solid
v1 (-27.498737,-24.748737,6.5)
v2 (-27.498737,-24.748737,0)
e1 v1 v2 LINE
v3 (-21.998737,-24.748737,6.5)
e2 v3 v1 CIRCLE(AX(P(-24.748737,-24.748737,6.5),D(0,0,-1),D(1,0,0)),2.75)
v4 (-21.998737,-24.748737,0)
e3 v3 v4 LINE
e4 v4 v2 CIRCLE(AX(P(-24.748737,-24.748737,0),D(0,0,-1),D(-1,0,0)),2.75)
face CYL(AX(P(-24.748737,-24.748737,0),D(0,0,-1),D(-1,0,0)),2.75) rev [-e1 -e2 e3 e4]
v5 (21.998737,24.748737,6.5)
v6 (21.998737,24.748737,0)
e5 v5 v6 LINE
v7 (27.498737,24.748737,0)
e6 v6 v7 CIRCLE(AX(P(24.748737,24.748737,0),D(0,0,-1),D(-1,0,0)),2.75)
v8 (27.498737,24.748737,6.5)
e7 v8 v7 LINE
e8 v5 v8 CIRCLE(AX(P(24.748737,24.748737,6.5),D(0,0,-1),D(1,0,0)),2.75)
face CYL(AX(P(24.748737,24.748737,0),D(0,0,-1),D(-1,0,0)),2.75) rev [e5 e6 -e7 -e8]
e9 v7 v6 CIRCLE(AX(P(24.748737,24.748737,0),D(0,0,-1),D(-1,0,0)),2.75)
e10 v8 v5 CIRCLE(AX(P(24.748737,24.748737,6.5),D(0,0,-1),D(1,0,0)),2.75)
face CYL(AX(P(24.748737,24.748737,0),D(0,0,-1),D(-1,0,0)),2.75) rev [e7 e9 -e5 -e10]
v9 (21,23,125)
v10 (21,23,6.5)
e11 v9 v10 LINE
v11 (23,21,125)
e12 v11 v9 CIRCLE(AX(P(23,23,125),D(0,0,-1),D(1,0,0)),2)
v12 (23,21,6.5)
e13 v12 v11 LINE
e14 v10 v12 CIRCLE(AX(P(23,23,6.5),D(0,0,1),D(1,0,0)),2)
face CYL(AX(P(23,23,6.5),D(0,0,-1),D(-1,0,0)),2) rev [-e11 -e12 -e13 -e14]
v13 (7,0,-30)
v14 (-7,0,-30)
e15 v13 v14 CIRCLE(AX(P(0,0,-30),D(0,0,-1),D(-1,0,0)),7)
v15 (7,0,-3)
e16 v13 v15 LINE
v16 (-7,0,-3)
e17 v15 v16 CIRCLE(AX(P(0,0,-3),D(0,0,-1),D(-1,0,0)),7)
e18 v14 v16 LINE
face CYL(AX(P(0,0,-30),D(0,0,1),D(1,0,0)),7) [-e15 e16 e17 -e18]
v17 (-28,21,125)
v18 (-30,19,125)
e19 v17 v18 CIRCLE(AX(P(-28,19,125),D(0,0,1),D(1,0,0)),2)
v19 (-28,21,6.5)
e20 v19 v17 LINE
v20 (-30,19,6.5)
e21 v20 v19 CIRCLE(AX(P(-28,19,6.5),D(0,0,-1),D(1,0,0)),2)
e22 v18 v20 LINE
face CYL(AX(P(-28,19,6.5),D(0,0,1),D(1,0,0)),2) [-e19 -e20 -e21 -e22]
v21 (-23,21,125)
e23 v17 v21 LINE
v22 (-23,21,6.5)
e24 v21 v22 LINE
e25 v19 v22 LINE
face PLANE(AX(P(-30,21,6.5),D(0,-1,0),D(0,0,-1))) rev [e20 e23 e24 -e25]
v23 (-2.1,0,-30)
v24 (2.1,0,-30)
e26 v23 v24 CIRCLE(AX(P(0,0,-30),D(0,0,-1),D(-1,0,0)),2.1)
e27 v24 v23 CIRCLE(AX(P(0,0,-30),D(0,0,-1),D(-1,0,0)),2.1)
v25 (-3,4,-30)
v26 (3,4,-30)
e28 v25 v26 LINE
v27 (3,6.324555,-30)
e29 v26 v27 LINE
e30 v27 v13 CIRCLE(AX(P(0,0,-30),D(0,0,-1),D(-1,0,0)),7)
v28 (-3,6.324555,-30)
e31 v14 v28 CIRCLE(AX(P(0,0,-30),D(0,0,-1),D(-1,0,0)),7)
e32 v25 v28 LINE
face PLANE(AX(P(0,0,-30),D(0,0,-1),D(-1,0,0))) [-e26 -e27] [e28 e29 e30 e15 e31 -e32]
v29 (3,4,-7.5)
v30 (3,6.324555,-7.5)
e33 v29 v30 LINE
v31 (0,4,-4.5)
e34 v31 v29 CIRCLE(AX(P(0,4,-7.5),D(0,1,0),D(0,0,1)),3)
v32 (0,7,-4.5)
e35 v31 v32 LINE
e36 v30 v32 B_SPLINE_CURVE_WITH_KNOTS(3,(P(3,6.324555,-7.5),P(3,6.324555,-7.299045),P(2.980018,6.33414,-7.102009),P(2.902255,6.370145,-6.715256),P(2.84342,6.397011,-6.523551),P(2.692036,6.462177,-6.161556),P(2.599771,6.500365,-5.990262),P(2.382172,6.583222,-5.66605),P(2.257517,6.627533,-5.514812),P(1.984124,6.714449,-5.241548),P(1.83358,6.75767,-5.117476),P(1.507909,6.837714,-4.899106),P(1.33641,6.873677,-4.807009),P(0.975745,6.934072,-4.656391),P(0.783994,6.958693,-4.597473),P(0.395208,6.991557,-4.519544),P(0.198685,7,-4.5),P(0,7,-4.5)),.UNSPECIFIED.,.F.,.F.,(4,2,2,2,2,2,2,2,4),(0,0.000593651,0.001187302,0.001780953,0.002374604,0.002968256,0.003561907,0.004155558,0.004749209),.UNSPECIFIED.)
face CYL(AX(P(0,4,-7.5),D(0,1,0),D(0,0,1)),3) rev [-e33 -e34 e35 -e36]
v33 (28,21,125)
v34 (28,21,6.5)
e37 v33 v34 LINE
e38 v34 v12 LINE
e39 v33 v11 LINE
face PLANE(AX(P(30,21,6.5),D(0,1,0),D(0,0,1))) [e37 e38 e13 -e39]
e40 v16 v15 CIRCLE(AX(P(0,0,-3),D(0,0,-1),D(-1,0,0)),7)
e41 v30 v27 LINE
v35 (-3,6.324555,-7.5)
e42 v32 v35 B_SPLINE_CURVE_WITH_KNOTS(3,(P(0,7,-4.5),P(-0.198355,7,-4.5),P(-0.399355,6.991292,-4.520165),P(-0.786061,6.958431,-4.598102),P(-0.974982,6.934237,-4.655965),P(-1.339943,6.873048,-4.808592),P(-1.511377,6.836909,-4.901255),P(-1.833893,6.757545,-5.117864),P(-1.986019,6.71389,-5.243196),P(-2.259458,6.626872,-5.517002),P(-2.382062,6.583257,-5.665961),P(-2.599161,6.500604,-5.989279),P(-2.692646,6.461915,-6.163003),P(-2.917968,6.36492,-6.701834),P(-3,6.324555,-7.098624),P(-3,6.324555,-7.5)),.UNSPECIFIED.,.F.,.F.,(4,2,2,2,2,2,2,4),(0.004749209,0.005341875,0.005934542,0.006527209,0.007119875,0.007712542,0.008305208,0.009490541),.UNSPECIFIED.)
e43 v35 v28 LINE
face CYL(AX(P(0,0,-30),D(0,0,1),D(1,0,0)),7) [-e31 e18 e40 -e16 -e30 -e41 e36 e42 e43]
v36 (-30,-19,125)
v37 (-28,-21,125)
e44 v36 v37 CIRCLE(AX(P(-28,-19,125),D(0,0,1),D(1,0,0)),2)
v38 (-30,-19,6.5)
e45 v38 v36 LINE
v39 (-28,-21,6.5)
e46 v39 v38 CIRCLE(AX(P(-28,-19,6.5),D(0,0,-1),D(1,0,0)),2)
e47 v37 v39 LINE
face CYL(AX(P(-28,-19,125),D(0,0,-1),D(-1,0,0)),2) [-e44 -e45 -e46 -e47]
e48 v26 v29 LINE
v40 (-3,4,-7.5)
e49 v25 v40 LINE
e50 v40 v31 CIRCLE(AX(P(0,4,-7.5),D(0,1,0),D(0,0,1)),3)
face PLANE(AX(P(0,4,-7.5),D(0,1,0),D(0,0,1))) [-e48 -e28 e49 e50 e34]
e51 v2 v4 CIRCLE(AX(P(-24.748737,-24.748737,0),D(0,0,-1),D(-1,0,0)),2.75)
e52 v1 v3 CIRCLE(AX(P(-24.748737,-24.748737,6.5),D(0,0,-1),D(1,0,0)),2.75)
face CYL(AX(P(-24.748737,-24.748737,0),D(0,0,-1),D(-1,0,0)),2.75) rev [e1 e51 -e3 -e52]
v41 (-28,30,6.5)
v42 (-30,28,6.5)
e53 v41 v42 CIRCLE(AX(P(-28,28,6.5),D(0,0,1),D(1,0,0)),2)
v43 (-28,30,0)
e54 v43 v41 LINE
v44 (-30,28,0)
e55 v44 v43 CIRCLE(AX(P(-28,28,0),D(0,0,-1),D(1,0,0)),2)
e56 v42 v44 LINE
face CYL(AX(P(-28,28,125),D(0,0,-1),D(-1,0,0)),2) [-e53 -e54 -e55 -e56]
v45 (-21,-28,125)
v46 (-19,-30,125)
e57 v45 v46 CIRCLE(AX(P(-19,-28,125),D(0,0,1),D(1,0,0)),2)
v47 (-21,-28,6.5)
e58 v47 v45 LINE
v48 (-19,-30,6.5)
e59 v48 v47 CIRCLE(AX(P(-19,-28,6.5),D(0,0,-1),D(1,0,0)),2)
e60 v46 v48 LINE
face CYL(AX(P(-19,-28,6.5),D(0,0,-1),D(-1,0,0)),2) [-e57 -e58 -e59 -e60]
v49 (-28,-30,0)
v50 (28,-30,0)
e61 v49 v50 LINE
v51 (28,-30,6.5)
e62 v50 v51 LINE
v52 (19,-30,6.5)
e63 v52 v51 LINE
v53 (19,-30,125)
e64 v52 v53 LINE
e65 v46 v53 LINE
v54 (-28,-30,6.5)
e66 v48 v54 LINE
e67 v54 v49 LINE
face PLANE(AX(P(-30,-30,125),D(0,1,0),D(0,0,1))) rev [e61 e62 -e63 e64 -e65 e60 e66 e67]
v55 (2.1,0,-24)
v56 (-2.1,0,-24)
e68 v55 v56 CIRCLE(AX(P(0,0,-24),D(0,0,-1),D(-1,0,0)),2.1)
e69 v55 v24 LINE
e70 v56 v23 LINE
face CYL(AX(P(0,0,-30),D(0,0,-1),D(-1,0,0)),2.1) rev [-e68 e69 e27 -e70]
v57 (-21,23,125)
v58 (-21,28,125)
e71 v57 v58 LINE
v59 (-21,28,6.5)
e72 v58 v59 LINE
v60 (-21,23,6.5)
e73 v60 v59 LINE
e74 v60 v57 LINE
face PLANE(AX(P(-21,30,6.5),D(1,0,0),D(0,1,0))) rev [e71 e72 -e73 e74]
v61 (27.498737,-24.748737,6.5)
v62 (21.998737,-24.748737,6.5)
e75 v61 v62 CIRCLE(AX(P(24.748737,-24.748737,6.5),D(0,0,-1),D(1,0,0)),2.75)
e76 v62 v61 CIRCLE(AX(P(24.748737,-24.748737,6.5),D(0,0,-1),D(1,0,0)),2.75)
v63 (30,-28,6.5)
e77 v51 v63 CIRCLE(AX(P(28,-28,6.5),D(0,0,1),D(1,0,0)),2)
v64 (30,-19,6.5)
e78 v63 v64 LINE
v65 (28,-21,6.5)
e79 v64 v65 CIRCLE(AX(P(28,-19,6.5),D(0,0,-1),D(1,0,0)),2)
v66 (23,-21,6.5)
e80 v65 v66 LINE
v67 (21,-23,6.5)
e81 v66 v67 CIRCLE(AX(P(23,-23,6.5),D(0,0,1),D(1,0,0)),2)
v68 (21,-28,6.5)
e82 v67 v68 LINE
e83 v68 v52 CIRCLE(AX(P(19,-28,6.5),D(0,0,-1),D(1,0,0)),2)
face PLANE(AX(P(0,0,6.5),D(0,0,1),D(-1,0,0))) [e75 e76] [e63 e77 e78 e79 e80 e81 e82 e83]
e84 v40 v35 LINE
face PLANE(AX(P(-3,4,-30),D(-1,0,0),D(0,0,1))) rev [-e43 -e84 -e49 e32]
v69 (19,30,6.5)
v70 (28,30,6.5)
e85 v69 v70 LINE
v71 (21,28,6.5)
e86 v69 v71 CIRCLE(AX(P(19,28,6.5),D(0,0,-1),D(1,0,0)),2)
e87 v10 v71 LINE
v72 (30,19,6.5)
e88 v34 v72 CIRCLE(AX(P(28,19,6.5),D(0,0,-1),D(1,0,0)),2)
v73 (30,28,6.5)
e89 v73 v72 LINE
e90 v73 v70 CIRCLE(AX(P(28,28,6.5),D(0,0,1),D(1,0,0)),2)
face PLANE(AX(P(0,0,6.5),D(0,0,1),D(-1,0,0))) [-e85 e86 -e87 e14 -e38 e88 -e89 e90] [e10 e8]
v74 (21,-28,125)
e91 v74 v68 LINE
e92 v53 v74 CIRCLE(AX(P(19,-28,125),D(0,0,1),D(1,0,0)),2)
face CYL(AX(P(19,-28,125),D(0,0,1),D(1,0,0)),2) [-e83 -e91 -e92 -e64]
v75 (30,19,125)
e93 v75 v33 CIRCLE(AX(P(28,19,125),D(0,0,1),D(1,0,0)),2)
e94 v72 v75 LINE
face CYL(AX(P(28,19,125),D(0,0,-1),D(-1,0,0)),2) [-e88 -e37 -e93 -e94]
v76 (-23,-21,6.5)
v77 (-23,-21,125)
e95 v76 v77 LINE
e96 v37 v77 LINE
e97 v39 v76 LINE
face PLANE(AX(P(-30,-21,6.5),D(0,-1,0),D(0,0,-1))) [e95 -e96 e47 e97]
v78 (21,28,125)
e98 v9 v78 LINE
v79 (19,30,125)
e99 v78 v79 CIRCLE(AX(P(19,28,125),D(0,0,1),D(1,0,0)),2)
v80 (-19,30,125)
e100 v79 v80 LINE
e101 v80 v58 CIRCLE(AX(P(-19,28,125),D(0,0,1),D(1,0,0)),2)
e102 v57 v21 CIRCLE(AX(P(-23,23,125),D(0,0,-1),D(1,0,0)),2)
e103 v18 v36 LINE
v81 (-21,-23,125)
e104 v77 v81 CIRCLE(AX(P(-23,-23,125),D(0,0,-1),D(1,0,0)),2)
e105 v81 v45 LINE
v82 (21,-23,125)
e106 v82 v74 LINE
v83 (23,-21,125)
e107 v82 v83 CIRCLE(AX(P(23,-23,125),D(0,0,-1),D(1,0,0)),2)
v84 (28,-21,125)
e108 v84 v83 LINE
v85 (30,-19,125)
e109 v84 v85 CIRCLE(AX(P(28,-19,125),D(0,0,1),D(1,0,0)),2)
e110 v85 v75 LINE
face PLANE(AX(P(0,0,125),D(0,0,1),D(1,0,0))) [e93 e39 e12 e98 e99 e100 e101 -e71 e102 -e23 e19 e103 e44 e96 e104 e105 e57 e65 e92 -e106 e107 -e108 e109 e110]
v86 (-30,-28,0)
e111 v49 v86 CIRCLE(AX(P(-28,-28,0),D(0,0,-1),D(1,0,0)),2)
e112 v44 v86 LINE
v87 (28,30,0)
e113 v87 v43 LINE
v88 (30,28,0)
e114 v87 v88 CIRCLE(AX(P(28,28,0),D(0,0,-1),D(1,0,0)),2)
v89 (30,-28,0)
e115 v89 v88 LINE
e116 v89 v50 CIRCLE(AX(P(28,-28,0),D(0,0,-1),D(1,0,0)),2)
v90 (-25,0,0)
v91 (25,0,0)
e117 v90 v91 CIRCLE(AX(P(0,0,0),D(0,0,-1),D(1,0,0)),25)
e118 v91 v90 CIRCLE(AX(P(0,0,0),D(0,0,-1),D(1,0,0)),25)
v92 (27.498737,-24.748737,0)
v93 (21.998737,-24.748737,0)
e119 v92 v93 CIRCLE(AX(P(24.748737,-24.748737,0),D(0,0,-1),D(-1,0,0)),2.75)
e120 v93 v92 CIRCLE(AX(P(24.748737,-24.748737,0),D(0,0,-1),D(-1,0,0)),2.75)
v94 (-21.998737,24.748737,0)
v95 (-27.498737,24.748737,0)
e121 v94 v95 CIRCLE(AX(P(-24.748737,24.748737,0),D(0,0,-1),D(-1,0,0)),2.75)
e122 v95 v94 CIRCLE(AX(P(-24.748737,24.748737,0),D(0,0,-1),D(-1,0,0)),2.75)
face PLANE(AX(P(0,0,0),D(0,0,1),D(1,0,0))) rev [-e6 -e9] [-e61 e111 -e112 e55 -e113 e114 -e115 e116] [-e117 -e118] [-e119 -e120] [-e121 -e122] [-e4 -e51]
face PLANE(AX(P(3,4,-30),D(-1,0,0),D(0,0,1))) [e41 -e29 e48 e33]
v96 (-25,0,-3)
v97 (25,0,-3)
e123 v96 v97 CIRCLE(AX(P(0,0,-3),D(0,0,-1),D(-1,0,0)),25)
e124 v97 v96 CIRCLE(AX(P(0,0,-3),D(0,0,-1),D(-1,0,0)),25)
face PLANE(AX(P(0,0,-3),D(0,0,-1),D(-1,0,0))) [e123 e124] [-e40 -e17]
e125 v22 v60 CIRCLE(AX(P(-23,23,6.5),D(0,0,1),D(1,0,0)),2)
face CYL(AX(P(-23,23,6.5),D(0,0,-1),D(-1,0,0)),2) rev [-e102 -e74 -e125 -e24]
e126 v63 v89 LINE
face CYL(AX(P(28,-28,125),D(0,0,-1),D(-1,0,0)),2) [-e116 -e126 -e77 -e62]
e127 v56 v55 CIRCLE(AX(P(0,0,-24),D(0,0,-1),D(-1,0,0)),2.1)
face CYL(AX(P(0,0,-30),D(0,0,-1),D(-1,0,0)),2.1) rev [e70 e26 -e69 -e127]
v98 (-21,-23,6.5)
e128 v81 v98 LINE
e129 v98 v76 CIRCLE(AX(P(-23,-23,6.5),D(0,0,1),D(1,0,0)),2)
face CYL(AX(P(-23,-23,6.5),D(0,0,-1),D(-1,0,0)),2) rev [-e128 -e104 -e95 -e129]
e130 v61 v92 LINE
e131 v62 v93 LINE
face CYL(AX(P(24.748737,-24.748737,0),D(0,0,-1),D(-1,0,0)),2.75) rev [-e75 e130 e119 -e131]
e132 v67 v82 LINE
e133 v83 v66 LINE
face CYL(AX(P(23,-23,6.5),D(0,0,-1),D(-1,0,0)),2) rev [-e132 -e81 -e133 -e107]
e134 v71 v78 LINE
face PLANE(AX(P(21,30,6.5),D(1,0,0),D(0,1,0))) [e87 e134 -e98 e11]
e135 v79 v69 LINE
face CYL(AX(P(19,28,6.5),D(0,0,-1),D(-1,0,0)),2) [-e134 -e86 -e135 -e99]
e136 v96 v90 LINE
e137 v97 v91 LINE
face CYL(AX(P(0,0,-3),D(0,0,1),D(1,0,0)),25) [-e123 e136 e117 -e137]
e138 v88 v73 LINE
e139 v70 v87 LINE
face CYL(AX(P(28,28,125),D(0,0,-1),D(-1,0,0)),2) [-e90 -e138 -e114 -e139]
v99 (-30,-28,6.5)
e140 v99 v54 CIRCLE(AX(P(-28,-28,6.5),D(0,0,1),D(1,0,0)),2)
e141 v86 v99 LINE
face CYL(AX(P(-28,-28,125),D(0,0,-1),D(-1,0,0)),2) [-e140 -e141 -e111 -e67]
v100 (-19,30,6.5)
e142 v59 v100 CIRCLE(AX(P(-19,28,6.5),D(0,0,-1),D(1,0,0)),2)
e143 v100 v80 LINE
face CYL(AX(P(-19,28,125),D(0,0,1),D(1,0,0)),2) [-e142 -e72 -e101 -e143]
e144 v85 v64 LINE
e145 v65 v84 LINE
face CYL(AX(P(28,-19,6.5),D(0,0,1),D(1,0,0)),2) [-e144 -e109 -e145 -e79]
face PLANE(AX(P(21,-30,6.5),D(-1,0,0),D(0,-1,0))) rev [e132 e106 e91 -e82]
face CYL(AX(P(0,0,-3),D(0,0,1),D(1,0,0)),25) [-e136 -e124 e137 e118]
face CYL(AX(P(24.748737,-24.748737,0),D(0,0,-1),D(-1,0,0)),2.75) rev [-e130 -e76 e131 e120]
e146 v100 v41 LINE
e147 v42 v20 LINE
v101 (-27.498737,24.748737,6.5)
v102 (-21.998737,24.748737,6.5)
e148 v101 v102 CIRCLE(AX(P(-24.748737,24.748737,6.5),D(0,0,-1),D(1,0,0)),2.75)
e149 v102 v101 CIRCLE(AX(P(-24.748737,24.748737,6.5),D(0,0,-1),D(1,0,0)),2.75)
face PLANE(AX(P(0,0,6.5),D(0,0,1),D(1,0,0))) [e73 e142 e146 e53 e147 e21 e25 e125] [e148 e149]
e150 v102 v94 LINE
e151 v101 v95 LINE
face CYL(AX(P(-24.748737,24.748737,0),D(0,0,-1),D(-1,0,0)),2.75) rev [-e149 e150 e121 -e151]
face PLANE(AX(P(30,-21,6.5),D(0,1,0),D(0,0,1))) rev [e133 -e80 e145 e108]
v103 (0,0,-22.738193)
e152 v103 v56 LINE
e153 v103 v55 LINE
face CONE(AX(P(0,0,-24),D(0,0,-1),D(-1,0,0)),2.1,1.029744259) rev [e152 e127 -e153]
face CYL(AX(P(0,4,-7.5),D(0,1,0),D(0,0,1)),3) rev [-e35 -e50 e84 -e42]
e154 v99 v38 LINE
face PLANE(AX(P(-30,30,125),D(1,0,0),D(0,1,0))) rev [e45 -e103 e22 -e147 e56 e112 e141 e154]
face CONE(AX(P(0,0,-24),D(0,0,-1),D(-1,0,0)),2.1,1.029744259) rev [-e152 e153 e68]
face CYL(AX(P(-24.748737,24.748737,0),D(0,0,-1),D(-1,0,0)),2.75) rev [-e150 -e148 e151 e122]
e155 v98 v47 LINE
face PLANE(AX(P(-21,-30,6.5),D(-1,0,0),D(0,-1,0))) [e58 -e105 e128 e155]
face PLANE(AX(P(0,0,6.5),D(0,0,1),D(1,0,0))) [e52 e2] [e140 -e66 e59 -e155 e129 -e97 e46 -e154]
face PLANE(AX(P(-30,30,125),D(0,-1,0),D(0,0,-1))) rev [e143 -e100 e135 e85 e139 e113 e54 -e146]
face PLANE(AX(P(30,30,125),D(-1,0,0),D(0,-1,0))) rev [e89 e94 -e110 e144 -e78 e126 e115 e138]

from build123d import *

# Parameters (mm, degrees)
SKETCH_1_W                  = 60
SKETCH_1_H                  = 60
EXTRUDE_1_DEPTH             = 125
SKETCH_2_R                  = 25
EXTRUDE_2_DEPTH             = 3
SKETCH_3_R                  = 7
EXTRUDE_3_DEPTH             = 27
CUT_EXTRUDE_1_DEPTH         = 3
HOLE_WIZARD_M5_1_D          = 4.2
HOLE_WIZARD_M5_1_DEPTH      = 6
HOLE_WIZARD_M5_1_TIP        = 1.2618073
HOLE_WIZARD_4_5_4_5_1_D     = 5.5
HOLE_WIZARD_4_5_4_5_1_DEPTH = 10
HOLE_WIZARD_4_5_4_5_1_TIP   = 1.652366702
SKETCH_10_W                 = 9
SKETCH_10_H                 = 9
CUT_EXTRUDE_2_DEPTH         = 118.5
MIRROR_2_COPY_1_SKETCH_W    = 9
MIRROR_2_COPY_1_SKETCH_H    = 9
MIRROR_2_COPY_1_DEPTH       = 118.5
FILLET_1_R                  = 2


with BuildPart() as part:
    # 草图1 → 凸台-拉伸1 (new body)
    with BuildSketch(Plane.XY):
        Rectangle(SKETCH_1_W, SKETCH_1_H)
    extrude(amount=EXTRUDE_1_DEPTH)

    # 草图2 → 凸台-拉伸2 (add)
    with BuildSketch(Plane(origin=(0, 0, 0), x_dir=(-1, 0, 0), z_dir=(0, 0, -1))):
        with Locations(Location((0, 0, 0), (0, 0, 180))):
            Circle(SKETCH_2_R)
    extrude(amount=EXTRUDE_2_DEPTH)

    # 草图3 → 凸台-拉伸3 (add)
    with BuildSketch(Plane(origin=(0, 0, -3), x_dir=(-1, 0, 0), z_dir=(0, 0, -1))):
        Circle(SKETCH_3_R)
    extrude(amount=EXTRUDE_3_DEPTH)

    # 草图4 → 切除-拉伸1 (cut)
    with BuildSketch(Plane(origin=(0, 7, 0), x_dir=(1, 0, 0), z_dir=(0, 1, 0))):
        with BuildLine():
            Line((3, 30), (3, 7.5))
            ThreePointArc((3, 7.5), (0, 4.5), (-3, 7.5))
            Line((-3, 7.5), (-3, 30))
            ThreePointArc((-3, 30), (0, 33), (3, 30))
        make_face()
    extrude(amount=-CUT_EXTRUDE_1_DEPTH, mode=Mode.SUBTRACT)

    # M5 螺纹孔1
    with Locations(Plane(origin=(0, 0, -30), x_dir=(-1, 0, 0), z_dir=(0, 0, -1))):
        with Locations((0, 0)):
            Hole(HOLE_WIZARD_M5_1_D / 2, depth=HOLE_WIZARD_M5_1_DEPTH)
            with Locations((0, 0, -(HOLE_WIZARD_M5_1_DEPTH + HOLE_WIZARD_M5_1_TIP / 2))):  # 118° drill point
                Cone(0, HOLE_WIZARD_M5_1_D / 2, HOLE_WIZARD_M5_1_TIP, mode=Mode.SUBTRACT)

    # Ø4.5 (4.5) 直径孔1
    with Locations(Plane(origin=(0, 0, 0), x_dir=(-1, 0, 0), z_dir=(0, 0, -1))):
        with Locations((-24.748737342, 24.748737342), (24.748737342, 24.748737342), (24.748737342, -24.748737342), (-24.748737342, -24.748737342)):
            Hole(HOLE_WIZARD_4_5_4_5_1_D / 2, depth=HOLE_WIZARD_4_5_4_5_1_DEPTH)
            with Locations((0, 0, -(HOLE_WIZARD_4_5_4_5_1_DEPTH + HOLE_WIZARD_4_5_4_5_1_TIP / 2))):  # 118° drill point
                Cone(0, HOLE_WIZARD_4_5_4_5_1_D / 2, HOLE_WIZARD_4_5_4_5_1_TIP, mode=Mode.SUBTRACT)

    # 草图10 → 切除-拉伸2 (cut)
    with BuildSketch(Plane.XY.offset(125)):
        with Locations((-25.5, 25.5)):
            Rectangle(SKETCH_10_W, SKETCH_10_H)
    cut_extrude_2 = extrude(amount=-CUT_EXTRUDE_2_DEPTH, mode=Mode.SUBTRACT)

    # 镜向1: 切除-拉伸2 across plane
    add(cut_extrude_2.mirror(Plane(origin=(0, 0, 0), x_dir=(0, 0, 1), z_dir=(1, 0, 0))), mode=Mode.SUBTRACT)

    # 镜向2: 切除-拉伸2 across plane
    add(cut_extrude_2.mirror(Plane.ZX), mode=Mode.SUBTRACT)

    # 镜向2 copy 1 sketch → 镜向2 copy 1 (cut)
    with BuildSketch(Plane(origin=(0, 0, 125), x_dir=(-1, 0, 0), z_dir=(0, 0, 1))):
        with Locations((-25.5, 25.5)):
            Rectangle(MIRROR_2_COPY_1_SKETCH_W, MIRROR_2_COPY_1_SKETCH_H)
    extrude(amount=-MIRROR_2_COPY_1_DEPTH, mode=Mode.SUBTRACT)

    # 圆角1
    fillet_1_edges = [part.edges().sort_by_distance(p)[0] for p in [
        (-30, -30, 3.25),
        (-30, -21, 65.75),
        (-21, -21, 65.75),
        (-21, -30, 65.75),
        (-30, 30, 3.25),
        (-30, 21, 65.75),
        (-21, 30, 65.75),
        (-21, 21, 65.75),
        (30, 30, 3.25),
        (30, 21, 65.75),
        (21, 21, 65.75),
        (21, 30, 65.75),
        (30, -30, 3.25),
        (30, -21, 65.75),
        (21, -30, 65.75),
        (21, -21, 65.75),
    ]]
    fillet(fillet_1_edges, radius=FILLET_1_R)


solid = part.part
